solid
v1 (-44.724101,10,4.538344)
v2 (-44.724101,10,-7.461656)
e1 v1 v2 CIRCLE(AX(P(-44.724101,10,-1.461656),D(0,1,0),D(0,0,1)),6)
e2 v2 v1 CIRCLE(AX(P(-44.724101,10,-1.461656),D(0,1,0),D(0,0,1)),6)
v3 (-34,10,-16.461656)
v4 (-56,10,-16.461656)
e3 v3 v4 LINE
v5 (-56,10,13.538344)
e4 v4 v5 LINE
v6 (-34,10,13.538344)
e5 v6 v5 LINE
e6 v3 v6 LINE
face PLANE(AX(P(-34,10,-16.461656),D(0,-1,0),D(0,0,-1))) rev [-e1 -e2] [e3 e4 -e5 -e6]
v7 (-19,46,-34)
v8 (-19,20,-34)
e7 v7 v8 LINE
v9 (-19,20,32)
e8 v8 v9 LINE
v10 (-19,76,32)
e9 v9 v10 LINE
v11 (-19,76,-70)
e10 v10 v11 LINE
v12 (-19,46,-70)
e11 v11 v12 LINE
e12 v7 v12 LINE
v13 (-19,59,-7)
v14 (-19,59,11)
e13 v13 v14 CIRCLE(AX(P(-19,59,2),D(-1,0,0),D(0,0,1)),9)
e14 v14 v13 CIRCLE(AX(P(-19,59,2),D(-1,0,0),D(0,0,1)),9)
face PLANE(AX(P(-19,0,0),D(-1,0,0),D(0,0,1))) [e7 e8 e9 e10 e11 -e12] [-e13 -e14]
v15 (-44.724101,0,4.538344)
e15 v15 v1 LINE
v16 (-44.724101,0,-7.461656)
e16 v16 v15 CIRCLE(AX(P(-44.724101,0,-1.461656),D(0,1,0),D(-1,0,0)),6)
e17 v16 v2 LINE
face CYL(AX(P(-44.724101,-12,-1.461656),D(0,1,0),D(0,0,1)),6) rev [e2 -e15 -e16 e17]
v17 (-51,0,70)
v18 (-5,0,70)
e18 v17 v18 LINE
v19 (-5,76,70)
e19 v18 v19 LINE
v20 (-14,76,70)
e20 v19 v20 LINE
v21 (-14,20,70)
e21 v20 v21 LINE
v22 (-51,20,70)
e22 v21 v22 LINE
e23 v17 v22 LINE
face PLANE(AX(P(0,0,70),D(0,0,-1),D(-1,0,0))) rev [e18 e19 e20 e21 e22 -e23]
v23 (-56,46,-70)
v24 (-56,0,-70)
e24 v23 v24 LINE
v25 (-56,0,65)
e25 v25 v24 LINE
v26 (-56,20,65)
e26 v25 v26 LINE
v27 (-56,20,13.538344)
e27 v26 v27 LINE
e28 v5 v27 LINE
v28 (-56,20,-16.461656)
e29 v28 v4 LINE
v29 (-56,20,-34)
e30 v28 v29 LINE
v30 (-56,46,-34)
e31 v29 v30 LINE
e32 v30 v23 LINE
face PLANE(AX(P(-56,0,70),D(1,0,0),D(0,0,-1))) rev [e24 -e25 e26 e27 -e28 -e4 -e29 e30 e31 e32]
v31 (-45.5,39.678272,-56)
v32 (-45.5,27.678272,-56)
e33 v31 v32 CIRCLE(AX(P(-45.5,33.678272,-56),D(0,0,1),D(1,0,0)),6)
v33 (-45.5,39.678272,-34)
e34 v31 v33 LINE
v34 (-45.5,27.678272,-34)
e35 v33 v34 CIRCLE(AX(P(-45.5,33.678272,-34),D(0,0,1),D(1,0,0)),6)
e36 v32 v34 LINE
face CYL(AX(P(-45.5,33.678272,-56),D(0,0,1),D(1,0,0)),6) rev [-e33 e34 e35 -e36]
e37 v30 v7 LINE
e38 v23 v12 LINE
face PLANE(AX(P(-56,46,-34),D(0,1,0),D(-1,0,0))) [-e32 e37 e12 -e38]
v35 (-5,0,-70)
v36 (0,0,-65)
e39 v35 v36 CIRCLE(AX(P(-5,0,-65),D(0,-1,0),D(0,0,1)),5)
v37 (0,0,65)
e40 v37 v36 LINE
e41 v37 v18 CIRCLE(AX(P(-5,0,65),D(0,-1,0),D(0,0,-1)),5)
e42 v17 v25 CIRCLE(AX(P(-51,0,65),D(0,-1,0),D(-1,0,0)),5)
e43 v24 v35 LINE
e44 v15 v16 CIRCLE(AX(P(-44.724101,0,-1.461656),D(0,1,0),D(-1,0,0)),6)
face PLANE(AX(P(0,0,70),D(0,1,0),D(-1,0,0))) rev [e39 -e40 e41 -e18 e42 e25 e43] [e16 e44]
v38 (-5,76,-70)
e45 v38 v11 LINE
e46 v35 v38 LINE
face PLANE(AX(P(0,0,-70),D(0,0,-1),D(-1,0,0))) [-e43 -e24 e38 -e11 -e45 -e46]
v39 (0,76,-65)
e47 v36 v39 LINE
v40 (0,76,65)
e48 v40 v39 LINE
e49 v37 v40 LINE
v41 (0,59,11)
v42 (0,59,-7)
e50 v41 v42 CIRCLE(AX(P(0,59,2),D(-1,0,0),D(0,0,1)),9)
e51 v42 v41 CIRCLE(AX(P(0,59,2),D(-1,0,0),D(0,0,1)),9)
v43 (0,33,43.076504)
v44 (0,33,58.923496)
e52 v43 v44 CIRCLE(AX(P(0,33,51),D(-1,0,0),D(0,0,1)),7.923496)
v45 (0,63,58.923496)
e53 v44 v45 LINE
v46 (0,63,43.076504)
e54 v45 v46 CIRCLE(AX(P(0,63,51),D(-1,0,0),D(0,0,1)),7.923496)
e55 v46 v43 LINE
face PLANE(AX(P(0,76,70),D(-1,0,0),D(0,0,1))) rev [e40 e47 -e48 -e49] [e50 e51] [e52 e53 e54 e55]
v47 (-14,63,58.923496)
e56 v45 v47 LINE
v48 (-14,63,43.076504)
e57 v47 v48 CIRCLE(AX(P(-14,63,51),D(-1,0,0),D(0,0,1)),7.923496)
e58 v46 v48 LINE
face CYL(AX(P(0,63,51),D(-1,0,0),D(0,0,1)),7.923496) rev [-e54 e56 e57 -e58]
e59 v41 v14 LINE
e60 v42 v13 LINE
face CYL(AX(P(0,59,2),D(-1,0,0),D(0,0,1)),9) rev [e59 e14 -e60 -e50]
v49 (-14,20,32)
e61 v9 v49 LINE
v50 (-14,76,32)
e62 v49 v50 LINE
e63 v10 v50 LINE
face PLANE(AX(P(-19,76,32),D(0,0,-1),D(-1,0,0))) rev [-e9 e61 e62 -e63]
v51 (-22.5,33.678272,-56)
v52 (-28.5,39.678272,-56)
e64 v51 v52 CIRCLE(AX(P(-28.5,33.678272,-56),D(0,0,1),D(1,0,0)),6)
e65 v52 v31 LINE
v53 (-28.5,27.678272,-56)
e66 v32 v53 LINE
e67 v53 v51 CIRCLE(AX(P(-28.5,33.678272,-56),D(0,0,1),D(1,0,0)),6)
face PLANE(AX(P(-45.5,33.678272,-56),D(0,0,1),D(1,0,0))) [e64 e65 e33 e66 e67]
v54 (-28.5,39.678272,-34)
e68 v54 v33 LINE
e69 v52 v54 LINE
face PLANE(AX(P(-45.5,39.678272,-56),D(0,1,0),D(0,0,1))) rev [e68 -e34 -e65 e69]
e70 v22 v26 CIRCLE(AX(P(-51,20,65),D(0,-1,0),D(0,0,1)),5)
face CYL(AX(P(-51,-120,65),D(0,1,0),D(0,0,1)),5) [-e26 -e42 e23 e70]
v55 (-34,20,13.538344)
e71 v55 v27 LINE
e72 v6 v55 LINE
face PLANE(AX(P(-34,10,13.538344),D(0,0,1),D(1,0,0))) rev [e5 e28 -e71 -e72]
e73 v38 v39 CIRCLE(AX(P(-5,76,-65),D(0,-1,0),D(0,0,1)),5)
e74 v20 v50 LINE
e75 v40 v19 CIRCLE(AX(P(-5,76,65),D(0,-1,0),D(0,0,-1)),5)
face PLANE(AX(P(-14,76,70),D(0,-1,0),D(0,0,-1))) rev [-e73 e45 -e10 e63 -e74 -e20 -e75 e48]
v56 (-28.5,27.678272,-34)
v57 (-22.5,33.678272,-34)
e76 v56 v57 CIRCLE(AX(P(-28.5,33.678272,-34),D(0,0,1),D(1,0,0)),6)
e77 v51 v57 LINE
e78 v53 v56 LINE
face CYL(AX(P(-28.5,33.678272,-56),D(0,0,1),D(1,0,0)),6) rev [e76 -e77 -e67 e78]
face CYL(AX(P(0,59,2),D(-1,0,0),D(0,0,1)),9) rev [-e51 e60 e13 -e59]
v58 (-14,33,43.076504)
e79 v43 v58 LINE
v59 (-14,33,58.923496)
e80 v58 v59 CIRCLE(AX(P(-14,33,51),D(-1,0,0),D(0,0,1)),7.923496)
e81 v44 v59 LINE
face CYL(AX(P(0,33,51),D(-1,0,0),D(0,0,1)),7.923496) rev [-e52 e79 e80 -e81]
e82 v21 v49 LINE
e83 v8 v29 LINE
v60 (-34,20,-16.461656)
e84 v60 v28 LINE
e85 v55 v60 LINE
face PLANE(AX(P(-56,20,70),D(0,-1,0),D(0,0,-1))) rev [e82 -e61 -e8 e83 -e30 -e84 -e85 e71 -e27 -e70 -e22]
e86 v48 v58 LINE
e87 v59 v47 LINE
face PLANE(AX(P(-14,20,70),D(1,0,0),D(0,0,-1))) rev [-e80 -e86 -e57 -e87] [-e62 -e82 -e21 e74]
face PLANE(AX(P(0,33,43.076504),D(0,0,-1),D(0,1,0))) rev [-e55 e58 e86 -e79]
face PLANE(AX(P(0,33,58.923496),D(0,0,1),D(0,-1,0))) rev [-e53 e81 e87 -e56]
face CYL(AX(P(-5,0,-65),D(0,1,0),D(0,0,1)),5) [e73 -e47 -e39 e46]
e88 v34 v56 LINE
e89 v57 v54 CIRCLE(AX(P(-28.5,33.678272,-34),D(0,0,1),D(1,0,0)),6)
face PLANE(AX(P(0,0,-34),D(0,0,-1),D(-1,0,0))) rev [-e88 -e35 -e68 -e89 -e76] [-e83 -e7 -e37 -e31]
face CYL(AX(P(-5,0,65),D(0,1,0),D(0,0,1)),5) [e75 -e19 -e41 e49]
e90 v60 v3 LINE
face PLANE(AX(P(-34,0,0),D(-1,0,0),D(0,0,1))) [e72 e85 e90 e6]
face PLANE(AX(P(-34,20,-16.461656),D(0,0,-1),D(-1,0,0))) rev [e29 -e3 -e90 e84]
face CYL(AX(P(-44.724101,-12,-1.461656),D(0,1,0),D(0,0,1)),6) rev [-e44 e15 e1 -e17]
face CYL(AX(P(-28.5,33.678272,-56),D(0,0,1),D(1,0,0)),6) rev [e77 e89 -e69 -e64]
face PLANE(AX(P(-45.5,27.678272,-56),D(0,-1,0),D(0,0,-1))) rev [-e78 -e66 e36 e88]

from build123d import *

# Parameters (mm, degrees)
BASE_ANGLE_BODY_DEPTH        = 70
FRONT_EDGE_RELIEF_CUT_DEPTH  = 118.524465538
LONG_EDGE_RELIEF_CUT_DEPTH   = 140
REAR_STEP_PAD_SKETCH_W       = 102
REAR_STEP_PAD_SKETCH_H       = 56
REAR_STEP_PAD_DEPTH          = 5
UPRIGHT_SLOT_CUT_DEPTH       = 112.534747949
PAD_RELIEF_SKETCH_R          = 9
PAD_RELIEF_CUT_DEPTH         = 110.749715262
REAR_BLOCK_SKETCH_W          = 37
REAR_BLOCK_SKETCH_H          = 26
REAR_BLOCK_DEPTH             = 36
REAR_POCKET_SKETCH_W         = 30
REAR_POCKET_SKETCH_H         = 10
REAR_POCKET_CUT_DEPTH        = 22
UPRIGHT_HOLE_SKETCH_R        = 6
UPRIGHT_HOLE_CUT_DEPTH       = 22
REAR_BLOCK_PROFILE_CUT_DEPTH = 22


with BuildPart() as part:
    # Base Angle Profile Sketch → Base Angle Body (new, symmetric)
    with BuildSketch(Plane.XY):
        Polygon((0, 0), (-56, 0), (-56, 20), (-14, 20), (-14, 76), (0, 76), align=None)
    extrude(amount=BASE_ANGLE_BODY_DEPTH, both=True)

    # Front Edge Relief Sketch → Front Edge Relief Cut (cut, through all)
    with BuildSketch(Plane(origin=(0, 76, 0), x_dir=(1, 0, 0), z_dir=(0, 1, 0))):
        with BuildLine():
            Line((-5, 70), (0, 70))
            Line((0, 70), (0, 65))
            ThreePointArc((0, 65), (-1.464466094, 68.535533906), (-5, 70))
        make_face()
        with BuildLine():
            Line((0, -70), (0, -65))
            ThreePointArc((0, -65), (-1.464466094, -68.535533906), (-5, -70))
            Line((-5, -70), (0, -70))
        make_face()
    extrude(amount=-FRONT_EDGE_RELIEF_CUT_DEPTH, mode=Mode.SUBTRACT)

    # Long Edge Relief Sketch → Long Edge Relief Cut (cut)
    with BuildSketch(Plane(origin=(0, 20, 0), x_dir=(1, 0, 0), z_dir=(0, 1, 0))):
        with BuildLine():
            Line((-56, -65), (-56, -70))
            Line((-56, -70), (-51, -70))
            ThreePointArc((-51, -70), (-54.535533906, -68.535533906), (-56, -65))
        make_face()
    extrude(amount=-LONG_EDGE_RELIEF_CUT_DEPTH, mode=Mode.SUBTRACT)

    # Rear Step Pad Sketch → Rear Step Pad (add)
    with BuildSketch(Plane.ZY.offset(14)):
        with Locations((-19, 48)):
            Rectangle(REAR_STEP_PAD_SKETCH_W, REAR_STEP_PAD_SKETCH_H)
    extrude(amount=REAR_STEP_PAD_DEPTH)

    # Upright Slot Sketch → Upright Slot Cut (cut, through all)
    with BuildSketch(Plane.ZY.offset(14)):
        with BuildLine():
            Line((43.076503739, 33), (43.076503739, 63))
            ThreePointArc((43.076503739, 63), (51, 70.923496261), (58.923496261, 63))
            Line((58.923496261, 63), (58.923496261, 33))
            ThreePointArc((58.923496261, 33), (51, 25.076503739), (43.076503739, 33))
        make_face()
    extrude(amount=-UPRIGHT_SLOT_CUT_DEPTH, mode=Mode.SUBTRACT)

    # Pad Relief Sketch → Pad Relief Cut (cut, through all)
    with BuildSketch(Plane.ZY.offset(19)):
        with Locations((2, 59)):
            Circle(PAD_RELIEF_SKETCH_R)
    extrude(amount=-PAD_RELIEF_CUT_DEPTH, mode=Mode.SUBTRACT)

    # Rear Block Sketch → Rear Block (add)
    with BuildSketch(Plane(origin=(0, 0, -70), x_dir=(-1, 0, 0), z_dir=(0, 0, -1))):
        with Locations((37.5, 33)):
            Rectangle(REAR_BLOCK_SKETCH_W, REAR_BLOCK_SKETCH_H)
    extrude(amount=-REAR_BLOCK_DEPTH)

    # Rear Pocket Sketch → Rear Pocket Cut (cut)
    with BuildSketch(Plane.ZY.offset(56)):
        with Locations((-1.461655613, 15)):
            Rectangle(REAR_POCKET_SKETCH_W, REAR_POCKET_SKETCH_H)
    extrude(amount=-REAR_POCKET_CUT_DEPTH, mode=Mode.SUBTRACT)

    # Upright Hole Sketch → Upright Hole Cut (cut)
    with BuildSketch(Plane(origin=(0, 10, 0), x_dir=(1, 0, 0), z_dir=(0, 1, 0))):
        with Locations(Location((-44.72410092, 1.461655613, 0), (0, 0, 270))):
            Circle(UPRIGHT_HOLE_SKETCH_R)
    extrude(amount=-UPRIGHT_HOLE_CUT_DEPTH, mode=Mode.SUBTRACT)

    # Rear Block Profile Sketch → Rear Block Profile Cut (cut)
    with BuildSketch(Plane.XY.offset(-34)):
        with BuildLine():
            Line((-45.5, 39.678271728), (-28.5, 39.678271728))
            ThreePointArc((-28.5, 39.678271728), (-22.5, 33.678271728), (-28.5, 27.678271728))
            Line((-28.5, 27.678271728), (-45.5, 27.678271728))
            ThreePointArc((-45.5, 27.678271728), (-51.5, 33.678271728), (-45.5, 39.678271728))
        make_face()
    extrude(amount=-REAR_BLOCK_PROFILE_CUT_DEPTH, mode=Mode.SUBTRACT)


solid = part.part
